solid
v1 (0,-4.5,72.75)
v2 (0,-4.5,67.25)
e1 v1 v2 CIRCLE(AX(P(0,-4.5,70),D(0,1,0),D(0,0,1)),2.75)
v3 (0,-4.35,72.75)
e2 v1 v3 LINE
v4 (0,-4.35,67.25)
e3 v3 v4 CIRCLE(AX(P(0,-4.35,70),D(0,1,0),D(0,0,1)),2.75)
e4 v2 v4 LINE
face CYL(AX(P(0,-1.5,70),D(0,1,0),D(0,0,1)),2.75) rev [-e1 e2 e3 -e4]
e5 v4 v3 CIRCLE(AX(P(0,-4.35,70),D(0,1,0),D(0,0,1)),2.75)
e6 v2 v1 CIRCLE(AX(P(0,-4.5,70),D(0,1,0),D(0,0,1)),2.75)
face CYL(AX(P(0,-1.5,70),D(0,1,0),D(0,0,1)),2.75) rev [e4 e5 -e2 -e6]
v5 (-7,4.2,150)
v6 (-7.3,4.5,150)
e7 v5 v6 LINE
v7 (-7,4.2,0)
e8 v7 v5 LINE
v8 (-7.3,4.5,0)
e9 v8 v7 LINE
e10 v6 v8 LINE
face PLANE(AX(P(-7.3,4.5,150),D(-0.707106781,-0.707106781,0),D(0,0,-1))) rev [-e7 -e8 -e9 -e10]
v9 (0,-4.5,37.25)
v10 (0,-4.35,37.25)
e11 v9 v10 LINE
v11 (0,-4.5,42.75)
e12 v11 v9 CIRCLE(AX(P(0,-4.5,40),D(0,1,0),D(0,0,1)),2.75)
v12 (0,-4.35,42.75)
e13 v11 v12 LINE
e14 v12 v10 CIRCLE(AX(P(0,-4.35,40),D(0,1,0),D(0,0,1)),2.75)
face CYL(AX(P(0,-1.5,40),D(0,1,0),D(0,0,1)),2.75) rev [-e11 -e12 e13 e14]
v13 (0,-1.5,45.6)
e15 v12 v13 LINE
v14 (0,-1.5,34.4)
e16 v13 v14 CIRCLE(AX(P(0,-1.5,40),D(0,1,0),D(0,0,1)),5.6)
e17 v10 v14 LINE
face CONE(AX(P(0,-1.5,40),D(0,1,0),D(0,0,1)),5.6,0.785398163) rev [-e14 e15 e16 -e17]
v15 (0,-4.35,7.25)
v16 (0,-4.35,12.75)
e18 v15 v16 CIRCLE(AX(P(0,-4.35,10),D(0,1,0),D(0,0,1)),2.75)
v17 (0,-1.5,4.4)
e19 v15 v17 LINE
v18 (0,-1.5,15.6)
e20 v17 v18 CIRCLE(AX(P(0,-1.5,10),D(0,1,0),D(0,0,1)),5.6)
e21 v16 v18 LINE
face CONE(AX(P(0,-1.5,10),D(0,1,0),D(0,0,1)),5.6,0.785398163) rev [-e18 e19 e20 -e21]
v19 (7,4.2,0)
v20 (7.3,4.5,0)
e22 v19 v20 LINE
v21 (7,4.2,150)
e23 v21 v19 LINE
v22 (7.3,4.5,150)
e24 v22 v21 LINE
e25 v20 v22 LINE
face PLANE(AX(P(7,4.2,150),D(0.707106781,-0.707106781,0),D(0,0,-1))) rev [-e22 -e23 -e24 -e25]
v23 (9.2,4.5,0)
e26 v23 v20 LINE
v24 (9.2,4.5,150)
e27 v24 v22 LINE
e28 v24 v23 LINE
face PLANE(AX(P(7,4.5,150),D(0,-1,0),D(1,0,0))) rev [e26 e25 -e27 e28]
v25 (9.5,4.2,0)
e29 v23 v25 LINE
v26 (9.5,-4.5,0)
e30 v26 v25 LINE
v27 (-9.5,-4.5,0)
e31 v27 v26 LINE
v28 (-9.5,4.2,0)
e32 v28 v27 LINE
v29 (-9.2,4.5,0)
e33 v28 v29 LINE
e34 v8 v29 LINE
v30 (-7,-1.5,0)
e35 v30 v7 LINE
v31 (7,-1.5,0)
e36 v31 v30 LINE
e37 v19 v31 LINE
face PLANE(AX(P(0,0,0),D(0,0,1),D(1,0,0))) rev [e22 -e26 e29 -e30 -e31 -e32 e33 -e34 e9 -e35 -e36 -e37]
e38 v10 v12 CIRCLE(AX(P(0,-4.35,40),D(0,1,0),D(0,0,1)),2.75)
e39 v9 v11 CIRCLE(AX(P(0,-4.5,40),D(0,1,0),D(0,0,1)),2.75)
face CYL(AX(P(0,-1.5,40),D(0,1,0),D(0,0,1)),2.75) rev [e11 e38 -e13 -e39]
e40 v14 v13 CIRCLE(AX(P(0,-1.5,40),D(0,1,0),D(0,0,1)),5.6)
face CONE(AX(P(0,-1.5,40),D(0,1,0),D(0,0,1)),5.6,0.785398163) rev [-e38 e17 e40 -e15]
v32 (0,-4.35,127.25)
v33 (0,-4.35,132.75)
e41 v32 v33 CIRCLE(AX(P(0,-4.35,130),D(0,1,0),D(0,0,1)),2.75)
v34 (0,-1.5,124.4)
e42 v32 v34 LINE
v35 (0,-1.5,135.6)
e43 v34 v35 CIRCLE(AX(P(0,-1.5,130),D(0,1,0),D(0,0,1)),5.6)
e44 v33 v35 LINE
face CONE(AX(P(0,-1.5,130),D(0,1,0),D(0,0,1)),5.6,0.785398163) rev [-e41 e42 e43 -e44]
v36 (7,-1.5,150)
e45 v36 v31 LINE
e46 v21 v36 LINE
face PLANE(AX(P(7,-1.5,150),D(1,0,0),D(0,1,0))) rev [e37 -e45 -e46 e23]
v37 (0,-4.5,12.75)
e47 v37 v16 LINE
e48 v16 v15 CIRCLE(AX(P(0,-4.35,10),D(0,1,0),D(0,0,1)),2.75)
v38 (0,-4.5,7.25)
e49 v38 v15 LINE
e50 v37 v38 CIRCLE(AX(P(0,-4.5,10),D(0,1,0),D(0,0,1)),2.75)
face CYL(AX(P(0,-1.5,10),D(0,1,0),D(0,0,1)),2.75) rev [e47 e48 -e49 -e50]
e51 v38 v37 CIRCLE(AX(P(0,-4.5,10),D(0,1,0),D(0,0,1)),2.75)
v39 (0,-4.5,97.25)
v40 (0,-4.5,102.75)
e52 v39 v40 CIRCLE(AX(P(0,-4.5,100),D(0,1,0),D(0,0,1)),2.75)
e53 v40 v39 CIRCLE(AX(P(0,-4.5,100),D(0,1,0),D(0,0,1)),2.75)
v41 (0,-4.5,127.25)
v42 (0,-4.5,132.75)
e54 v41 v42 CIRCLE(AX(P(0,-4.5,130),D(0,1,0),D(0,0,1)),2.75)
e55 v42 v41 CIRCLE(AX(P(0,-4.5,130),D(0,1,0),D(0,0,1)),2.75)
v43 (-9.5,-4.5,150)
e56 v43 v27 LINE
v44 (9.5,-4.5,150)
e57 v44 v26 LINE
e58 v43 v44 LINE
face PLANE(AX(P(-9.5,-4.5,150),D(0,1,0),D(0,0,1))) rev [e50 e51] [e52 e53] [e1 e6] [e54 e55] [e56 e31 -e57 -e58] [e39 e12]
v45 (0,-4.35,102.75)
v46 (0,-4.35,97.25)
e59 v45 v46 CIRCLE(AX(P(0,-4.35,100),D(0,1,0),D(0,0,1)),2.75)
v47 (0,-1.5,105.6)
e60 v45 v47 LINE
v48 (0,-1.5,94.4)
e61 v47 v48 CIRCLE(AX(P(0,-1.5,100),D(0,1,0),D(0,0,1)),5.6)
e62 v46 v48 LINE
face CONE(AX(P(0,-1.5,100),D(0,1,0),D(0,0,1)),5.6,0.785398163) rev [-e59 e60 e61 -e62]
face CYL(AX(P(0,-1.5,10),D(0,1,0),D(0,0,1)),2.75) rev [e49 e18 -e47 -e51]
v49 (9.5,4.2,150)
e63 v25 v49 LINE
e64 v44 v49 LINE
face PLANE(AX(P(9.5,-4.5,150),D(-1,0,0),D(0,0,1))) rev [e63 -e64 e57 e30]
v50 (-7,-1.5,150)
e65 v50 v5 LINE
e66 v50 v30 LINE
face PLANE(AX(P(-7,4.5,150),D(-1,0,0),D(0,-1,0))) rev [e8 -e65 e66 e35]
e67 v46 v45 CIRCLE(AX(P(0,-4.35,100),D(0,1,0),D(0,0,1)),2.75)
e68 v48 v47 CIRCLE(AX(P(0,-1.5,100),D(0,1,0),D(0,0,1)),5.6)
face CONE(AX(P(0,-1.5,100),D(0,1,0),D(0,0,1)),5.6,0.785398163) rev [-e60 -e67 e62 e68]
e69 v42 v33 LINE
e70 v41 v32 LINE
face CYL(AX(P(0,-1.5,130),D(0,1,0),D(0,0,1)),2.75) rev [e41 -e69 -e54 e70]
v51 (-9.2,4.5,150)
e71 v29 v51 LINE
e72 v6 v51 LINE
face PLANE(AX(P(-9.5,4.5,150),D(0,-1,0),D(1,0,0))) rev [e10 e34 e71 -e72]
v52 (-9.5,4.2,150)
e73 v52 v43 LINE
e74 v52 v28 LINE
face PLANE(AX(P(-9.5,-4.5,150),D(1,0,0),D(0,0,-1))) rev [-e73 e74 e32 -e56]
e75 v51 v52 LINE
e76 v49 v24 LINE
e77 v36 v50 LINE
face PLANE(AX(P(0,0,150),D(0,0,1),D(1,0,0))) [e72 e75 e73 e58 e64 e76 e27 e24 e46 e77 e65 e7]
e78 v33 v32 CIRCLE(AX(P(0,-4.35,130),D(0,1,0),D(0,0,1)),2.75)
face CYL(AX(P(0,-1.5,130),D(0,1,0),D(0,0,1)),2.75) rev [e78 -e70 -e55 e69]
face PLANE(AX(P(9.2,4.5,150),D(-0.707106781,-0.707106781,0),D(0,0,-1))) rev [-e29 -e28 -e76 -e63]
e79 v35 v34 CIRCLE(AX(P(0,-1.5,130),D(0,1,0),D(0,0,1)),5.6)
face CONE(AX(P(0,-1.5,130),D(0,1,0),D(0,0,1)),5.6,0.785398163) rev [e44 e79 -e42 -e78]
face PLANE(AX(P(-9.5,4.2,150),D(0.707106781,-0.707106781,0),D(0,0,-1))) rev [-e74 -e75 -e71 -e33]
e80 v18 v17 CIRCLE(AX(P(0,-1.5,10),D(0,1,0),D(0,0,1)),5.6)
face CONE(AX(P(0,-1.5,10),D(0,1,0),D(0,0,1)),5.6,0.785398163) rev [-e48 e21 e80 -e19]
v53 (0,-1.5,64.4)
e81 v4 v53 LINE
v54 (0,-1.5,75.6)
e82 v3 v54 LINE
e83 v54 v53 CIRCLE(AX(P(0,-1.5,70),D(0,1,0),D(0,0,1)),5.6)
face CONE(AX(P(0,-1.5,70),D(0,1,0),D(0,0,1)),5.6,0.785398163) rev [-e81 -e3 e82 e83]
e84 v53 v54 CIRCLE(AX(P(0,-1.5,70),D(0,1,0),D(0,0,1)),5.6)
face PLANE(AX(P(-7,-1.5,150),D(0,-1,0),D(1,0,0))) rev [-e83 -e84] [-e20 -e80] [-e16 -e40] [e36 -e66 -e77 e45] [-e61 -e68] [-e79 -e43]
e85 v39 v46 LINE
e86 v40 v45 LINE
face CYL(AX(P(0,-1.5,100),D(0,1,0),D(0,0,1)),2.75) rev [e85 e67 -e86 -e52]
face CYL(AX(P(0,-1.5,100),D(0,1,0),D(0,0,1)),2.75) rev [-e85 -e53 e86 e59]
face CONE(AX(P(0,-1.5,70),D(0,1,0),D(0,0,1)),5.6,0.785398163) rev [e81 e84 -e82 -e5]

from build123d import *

# Parameters (mm, degrees)
BOSS_EXTRUDE1_DEPTH                          = 150
HOLE_SIZE_PER_PHILLIPS_SLOTTED_COUNT_2_COUNT = 2
HOLE_SIZE_PER_PHILLIPS_SLOTTED_COUNT_2_PITCH = 30
LPATTERN1_COUNT                              = 4
LPATTERN1_PITCH                              = 30
CHAMFER1_SIZE                                = 0.3


with BuildPart() as part:
    # Sketch1 → Boss-Extrude1 (new body)
    with BuildSketch(Plane.XY):
        Polygon((-7, 4.5), (-7, -1.5), (7, -1.5), (7, 4.5), (9.5, 4.5), (9.5, -4.5), (-9.5, -4.5), (-9.5, 4.5), align=None)
    extrude(amount=BOSS_EXTRUDE1_DEPTH)

    # Sketch5 → Hole size per Phillips slotted countersunk wood screw type 1 (revolve, cut)
    with BuildSketch(Plane(origin=(0, -1.5, 10), x_dir=(0, 0, 1), z_dir=(1, 0, 0))):
        Polygon((0, 0), (0, 3), (2.75, 3), (2.75, 2.85), (5.6, 0), align=None)
    hole_size_per_phillips_slotted_countersu = revolve(axis=Axis((0, 4.85, 10), (0, -1, 0)), mode=Mode.SUBTRACT)

    # Hole size per Phillips slotted count 2: Hole size per Phillips slotted countersunk wood screw type 1 ×2
    with Locations(*[(0, 0, i * HOLE_SIZE_PER_PHILLIPS_SLOTTED_COUNT_2_PITCH) for i in range(1, HOLE_SIZE_PER_PHILLIPS_SLOTTED_COUNT_2_COUNT)]):
        add(hole_size_per_phillips_slotted_countersu, mode=Mode.SUBTRACT)

    # LPattern1: Hole size per Phillips slotted countersunk wood screw type 1 ×4
    with Locations(*[(0, 0, i * LPATTERN1_PITCH) for i in range(1, LPATTERN1_COUNT)]):
        add(hole_size_per_phillips_slotted_countersu, mode=Mode.SUBTRACT)

    # LPattern1 copy 1 sketch → LPattern1 copy 1 (revolve, cut)
    with BuildSketch(Plane(origin=(0, -1.5, 70), x_dir=(0, 0, 1), z_dir=(1, 0, 0))):
        Polygon((0, 0), (0, 3), (2.75, 3), (2.75, 2.85), (5.6, 0), align=None)
    revolve(axis=Axis((0, 4.85, 70), (0, -1, 0)), mode=Mode.SUBTRACT)

    # LPattern1 copy 2 sketch → LPattern1 copy 2 (revolve, cut)
    with BuildSketch(Plane(origin=(0, -1.5, 100), x_dir=(0, 0, 1), z_dir=(1, 0, 0))):
        Polygon((0, 0), (0, 3), (2.75, 3), (2.75, 2.85), (5.6, 0), align=None)
    revolve(axis=Axis((0, 4.85, 100), (0, -1, 0)), mode=Mode.SUBTRACT)

    # LPattern1 copy 3 sketch → LPattern1 copy 3 (revolve, cut)
    with BuildSketch(Plane(origin=(0, -1.5, 130), x_dir=(0, 0, 1), z_dir=(1, 0, 0))):
        Polygon((0, 0), (0, 3), (2.75, 3), (2.75, 2.85), (5.6, 0), align=None)
    revolve(axis=Axis((0, 4.85, 130), (0, -1, 0)), mode=Mode.SUBTRACT)

    # Chamfer1
    chamfer1_edges = [part.edges().sort_by_distance(p)[0] for p in [
        (9.5, 4.5, 75),
        (-9.5, 4.5, 75),
        (-7, 4.5, 75),
        (7, 4.5, 75),
    ]]
    chamfer(chamfer1_edges, length=CHAMFER1_SIZE)


solid = part.part
